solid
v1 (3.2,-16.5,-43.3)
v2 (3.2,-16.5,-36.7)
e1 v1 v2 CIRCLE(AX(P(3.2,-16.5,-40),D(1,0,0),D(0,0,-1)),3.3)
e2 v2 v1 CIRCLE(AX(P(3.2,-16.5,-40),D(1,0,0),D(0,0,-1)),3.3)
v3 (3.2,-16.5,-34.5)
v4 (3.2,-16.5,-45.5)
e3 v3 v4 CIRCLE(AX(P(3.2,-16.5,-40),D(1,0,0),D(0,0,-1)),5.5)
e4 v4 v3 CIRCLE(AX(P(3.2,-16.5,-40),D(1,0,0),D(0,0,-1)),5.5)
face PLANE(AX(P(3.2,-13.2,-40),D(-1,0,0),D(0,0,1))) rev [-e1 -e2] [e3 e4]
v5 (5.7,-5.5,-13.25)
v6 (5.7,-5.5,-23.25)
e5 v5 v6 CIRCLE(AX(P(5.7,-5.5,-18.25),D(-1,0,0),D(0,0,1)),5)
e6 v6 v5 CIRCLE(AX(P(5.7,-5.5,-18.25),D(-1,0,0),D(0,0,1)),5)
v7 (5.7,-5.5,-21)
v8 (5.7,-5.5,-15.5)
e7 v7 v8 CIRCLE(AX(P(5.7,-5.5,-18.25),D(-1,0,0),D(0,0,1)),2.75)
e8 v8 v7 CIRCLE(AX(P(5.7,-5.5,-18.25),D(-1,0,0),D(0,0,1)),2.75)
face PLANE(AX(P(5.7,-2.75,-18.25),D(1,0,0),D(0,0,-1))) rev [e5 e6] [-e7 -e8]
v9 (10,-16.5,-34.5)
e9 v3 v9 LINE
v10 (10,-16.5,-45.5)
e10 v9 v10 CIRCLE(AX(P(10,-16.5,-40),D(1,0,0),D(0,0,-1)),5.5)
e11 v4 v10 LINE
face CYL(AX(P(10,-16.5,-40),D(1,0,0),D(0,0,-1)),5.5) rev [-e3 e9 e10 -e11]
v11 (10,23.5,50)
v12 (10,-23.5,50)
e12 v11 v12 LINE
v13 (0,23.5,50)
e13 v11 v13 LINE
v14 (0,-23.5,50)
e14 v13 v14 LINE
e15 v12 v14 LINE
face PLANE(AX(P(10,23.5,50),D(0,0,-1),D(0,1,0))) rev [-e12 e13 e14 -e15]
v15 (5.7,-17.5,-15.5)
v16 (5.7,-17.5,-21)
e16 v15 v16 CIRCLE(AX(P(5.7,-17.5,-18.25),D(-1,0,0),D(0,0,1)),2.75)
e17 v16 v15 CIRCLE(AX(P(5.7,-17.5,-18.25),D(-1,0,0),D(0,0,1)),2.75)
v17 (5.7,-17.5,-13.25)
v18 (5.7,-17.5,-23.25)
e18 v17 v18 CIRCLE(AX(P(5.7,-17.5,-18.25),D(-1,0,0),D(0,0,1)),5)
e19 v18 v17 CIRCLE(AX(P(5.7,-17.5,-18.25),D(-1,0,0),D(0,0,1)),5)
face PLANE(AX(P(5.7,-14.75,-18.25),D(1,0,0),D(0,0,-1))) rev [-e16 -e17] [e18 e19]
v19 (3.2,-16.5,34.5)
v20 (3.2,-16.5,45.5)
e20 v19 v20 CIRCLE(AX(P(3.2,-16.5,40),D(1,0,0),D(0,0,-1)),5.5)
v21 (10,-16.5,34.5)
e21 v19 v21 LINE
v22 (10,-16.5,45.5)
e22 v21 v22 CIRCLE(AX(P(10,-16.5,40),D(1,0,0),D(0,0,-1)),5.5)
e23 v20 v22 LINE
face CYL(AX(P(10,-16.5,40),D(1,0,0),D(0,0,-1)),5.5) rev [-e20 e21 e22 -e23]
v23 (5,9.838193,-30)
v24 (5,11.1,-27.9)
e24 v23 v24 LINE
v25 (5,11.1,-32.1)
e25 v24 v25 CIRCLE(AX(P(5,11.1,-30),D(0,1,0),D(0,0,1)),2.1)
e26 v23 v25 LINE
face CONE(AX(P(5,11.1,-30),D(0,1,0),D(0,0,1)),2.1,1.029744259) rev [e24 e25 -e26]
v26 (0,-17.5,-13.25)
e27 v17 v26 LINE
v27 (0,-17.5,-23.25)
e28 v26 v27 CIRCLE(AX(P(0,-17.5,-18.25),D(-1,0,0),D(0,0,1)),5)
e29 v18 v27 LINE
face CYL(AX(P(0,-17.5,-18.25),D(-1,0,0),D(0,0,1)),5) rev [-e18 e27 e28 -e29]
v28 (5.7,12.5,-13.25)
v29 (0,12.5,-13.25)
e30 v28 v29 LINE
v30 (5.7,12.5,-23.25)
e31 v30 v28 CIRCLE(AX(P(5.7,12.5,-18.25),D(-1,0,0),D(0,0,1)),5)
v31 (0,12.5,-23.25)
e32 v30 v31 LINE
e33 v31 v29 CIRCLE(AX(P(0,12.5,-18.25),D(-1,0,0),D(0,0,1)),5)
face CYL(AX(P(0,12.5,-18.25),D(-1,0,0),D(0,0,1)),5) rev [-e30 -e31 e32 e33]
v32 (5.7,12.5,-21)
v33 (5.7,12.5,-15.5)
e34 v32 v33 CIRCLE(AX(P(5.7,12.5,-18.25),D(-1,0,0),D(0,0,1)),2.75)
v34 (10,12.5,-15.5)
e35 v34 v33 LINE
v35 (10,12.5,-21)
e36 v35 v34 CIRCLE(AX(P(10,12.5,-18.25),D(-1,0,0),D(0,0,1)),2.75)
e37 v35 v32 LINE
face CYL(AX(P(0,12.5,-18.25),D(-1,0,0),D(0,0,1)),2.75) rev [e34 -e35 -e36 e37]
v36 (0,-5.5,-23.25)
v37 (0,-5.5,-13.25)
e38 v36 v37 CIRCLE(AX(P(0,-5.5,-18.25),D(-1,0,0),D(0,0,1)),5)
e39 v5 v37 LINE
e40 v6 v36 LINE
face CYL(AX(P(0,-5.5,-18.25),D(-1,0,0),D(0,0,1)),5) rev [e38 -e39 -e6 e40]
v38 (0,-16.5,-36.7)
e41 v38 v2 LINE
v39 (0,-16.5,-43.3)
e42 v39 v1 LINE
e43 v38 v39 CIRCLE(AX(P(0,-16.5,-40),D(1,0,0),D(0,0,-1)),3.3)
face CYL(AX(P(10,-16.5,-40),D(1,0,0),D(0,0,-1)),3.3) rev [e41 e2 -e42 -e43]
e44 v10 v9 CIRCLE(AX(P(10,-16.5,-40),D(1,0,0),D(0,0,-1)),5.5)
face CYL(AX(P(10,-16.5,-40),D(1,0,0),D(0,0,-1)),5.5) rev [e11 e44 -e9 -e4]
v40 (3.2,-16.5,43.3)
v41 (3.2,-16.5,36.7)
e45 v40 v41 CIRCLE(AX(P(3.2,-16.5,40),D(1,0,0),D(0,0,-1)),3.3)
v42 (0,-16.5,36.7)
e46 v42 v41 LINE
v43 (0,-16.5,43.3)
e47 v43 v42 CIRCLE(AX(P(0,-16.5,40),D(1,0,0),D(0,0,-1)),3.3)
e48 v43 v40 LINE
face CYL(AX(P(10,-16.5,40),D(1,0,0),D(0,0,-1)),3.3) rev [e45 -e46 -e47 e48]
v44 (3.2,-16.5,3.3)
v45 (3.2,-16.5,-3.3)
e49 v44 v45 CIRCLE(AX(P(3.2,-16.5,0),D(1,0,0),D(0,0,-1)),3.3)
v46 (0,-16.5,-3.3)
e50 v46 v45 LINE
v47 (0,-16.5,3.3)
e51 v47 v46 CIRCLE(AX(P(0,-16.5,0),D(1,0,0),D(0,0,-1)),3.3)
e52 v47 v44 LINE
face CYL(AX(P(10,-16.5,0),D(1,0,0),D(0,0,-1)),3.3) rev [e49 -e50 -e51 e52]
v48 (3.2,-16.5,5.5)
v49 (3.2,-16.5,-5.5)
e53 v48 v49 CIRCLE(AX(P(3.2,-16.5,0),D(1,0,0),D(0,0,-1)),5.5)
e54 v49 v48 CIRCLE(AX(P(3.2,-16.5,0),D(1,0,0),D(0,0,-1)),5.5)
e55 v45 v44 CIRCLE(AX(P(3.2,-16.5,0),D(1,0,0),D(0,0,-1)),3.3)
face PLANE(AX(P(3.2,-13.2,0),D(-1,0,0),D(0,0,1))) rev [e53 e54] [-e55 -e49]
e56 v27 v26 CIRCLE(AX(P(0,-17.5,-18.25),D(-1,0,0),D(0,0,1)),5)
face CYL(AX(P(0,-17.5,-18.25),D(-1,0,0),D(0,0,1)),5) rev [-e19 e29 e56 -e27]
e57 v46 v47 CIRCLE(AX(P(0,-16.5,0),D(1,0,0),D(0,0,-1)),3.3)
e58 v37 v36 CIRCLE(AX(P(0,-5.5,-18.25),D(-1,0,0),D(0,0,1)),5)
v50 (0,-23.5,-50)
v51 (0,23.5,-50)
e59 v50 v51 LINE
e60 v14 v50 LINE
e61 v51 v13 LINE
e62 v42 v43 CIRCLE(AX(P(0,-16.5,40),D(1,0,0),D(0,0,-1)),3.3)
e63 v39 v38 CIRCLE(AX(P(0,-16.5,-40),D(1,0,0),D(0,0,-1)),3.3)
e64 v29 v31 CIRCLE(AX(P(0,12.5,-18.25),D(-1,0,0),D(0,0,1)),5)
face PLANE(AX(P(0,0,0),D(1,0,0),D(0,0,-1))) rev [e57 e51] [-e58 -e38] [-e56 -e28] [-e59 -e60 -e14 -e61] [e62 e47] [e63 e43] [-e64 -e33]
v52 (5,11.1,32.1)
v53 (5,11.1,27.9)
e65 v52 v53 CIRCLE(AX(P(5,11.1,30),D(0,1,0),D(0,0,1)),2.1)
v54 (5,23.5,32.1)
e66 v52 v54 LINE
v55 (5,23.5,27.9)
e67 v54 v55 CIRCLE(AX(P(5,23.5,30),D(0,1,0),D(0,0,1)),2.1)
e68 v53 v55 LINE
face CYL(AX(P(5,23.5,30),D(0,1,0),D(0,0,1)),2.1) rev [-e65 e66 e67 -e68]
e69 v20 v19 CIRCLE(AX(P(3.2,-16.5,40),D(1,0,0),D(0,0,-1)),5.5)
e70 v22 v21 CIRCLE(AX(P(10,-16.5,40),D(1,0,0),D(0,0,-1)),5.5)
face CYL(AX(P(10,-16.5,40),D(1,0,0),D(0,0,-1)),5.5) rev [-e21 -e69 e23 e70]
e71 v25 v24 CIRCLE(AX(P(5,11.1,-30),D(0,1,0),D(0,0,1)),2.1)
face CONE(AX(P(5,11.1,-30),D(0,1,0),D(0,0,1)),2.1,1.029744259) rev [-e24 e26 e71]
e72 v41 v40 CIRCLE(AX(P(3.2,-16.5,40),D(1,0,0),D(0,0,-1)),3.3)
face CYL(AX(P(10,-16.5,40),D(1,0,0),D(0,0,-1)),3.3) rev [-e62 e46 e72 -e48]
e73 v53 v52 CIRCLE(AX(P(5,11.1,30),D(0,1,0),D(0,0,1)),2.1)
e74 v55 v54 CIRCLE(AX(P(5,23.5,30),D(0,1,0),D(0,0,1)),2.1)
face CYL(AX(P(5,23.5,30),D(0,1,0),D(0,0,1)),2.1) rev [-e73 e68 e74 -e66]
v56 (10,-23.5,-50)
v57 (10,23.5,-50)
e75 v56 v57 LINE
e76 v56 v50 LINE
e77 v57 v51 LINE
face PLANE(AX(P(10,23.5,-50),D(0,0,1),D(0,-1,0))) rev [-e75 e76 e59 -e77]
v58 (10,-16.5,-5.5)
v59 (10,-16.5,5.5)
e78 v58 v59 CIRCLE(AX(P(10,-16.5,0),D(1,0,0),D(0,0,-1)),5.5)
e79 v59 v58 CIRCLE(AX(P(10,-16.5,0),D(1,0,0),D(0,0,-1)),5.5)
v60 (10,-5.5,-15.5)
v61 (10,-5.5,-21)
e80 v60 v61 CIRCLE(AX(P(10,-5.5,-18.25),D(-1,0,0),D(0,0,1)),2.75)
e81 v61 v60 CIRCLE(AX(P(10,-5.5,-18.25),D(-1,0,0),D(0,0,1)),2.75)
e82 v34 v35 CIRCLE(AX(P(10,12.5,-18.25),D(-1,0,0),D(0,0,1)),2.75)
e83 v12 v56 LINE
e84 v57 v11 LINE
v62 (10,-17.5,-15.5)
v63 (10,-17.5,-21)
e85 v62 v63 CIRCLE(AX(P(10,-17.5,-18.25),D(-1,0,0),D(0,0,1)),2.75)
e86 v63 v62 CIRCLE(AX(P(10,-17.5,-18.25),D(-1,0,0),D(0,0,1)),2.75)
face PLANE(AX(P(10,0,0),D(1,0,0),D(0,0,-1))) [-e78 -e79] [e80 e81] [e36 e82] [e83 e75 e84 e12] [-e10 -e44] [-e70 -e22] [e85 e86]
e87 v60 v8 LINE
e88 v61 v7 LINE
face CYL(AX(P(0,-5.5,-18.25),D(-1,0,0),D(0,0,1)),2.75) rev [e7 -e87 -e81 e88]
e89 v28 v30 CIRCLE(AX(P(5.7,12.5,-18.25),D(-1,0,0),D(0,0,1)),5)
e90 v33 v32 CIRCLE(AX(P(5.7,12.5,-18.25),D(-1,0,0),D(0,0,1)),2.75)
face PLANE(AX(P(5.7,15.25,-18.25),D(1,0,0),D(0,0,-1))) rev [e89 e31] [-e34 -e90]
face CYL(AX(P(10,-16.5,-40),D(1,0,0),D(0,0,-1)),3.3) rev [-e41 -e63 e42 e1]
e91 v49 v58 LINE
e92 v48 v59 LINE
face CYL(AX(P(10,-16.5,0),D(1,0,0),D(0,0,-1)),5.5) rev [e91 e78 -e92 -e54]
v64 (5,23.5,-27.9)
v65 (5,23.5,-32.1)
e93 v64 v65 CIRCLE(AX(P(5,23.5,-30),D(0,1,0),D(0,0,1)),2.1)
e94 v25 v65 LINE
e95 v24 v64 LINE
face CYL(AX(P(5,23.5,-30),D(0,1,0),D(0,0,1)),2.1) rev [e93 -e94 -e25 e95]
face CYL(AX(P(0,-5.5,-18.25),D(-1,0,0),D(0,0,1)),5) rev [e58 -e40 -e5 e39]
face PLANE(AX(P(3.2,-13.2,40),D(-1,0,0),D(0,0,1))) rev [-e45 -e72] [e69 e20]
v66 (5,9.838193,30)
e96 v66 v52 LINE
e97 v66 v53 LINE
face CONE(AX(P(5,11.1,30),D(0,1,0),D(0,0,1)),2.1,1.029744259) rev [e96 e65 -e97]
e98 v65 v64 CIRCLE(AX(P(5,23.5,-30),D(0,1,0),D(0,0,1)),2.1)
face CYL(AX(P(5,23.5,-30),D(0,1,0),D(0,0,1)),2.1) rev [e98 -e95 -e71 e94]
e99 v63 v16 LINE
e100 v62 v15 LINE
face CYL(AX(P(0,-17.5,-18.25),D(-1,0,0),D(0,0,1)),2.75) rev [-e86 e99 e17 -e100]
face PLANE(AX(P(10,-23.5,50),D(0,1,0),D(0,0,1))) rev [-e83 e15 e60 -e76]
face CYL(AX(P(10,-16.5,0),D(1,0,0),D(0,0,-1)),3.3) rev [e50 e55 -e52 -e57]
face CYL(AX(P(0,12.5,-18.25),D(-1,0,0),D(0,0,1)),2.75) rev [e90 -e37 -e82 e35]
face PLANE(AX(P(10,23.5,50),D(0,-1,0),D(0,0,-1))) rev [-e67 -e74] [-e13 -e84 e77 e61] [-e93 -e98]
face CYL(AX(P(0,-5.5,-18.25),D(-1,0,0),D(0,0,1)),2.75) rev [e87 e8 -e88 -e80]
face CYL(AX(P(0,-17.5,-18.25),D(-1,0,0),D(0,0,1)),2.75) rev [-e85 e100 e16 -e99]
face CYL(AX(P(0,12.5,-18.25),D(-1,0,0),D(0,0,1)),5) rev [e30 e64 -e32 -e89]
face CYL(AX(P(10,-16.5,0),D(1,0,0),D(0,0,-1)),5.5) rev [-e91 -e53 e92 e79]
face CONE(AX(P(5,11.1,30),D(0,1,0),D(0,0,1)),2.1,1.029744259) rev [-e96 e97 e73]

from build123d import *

# Parameters (mm, degrees)
SKETCH_1_W                = 100
SKETCH_1_H                = 47
EXTRUDE_1_DEPTH           = 10
HOLE_WIZARD_1_D           = 6.6
HOLE_WIZARD_1_DEPTH       = 15
HOLE_WIZARD_1_CBORE_D     = 11
HOLE_WIZARD_1_CBORE_DEPTH = 6.8
HOLE_WIZARD_1_TIP         = 1.982840043
HOLE_WIZARD_2_D           = 5.5
HOLE_WIZARD_2_CBORE_D     = 10
HOLE_WIZARD_2_CBORE_DEPTH = 5.7
HOLE_WIZARD_M5_1_D        = 4.2
HOLE_WIZARD_M5_1_DEPTH    = 12.4
HOLE_WIZARD_M5_1_TIP      = 1.2618073


with BuildPart() as part:
    # 草图1 → 凸台-拉伸1 (new body)
    with BuildSketch(Plane(origin=(0, 0, 0), x_dir=(0, 0, -1), z_dir=(1, 0, 0))):
        Rectangle(SKETCH_1_W, SKETCH_1_H)
    extrude(amount=EXTRUDE_1_DEPTH)

    # 打孔尺寸(%根据)内六角圆柱头螺钉的类型1
    with Locations(Plane(origin=(10, 0, 0), x_dir=(0, 0, -1), z_dir=(1, 0, 0))):
        with Locations((-40, -16.5), (0, -16.5), (40, -16.5)):
            CounterBoreHole(HOLE_WIZARD_1_D / 2, HOLE_WIZARD_1_CBORE_D / 2, HOLE_WIZARD_1_CBORE_DEPTH, depth=HOLE_WIZARD_1_DEPTH)
            with Locations((0, 0, -(HOLE_WIZARD_1_DEPTH + HOLE_WIZARD_1_TIP / 2))):  # 118° drill point
                Cone(0, HOLE_WIZARD_1_D / 2, HOLE_WIZARD_1_TIP, mode=Mode.SUBTRACT)

    # 打孔尺寸(%根据)内六角圆柱头螺钉的类型2 (through all)
    with Locations(Plane.ZY):
        with Locations((-18.25, 12.5), (-18.25, -5.5), (-18.25, -17.5)):
            CounterBoreHole(HOLE_WIZARD_2_D / 2, HOLE_WIZARD_2_CBORE_D / 2, HOLE_WIZARD_2_CBORE_DEPTH)

    # M5 螺纹孔1
    with Locations(Plane(origin=(0, 23.5, 0), x_dir=(1, 0, 0), z_dir=(0, 1, 0))):
        with Locations((5, -30), (5, 30)):
            Hole(HOLE_WIZARD_M5_1_D / 2, depth=HOLE_WIZARD_M5_1_DEPTH)
            with Locations((0, 0, -(HOLE_WIZARD_M5_1_DEPTH + HOLE_WIZARD_M5_1_TIP / 2))):  # 118° drill point
                Cone(0, HOLE_WIZARD_M5_1_D / 2, HOLE_WIZARD_M5_1_TIP, mode=Mode.SUBTRACT)


solid = part.part
